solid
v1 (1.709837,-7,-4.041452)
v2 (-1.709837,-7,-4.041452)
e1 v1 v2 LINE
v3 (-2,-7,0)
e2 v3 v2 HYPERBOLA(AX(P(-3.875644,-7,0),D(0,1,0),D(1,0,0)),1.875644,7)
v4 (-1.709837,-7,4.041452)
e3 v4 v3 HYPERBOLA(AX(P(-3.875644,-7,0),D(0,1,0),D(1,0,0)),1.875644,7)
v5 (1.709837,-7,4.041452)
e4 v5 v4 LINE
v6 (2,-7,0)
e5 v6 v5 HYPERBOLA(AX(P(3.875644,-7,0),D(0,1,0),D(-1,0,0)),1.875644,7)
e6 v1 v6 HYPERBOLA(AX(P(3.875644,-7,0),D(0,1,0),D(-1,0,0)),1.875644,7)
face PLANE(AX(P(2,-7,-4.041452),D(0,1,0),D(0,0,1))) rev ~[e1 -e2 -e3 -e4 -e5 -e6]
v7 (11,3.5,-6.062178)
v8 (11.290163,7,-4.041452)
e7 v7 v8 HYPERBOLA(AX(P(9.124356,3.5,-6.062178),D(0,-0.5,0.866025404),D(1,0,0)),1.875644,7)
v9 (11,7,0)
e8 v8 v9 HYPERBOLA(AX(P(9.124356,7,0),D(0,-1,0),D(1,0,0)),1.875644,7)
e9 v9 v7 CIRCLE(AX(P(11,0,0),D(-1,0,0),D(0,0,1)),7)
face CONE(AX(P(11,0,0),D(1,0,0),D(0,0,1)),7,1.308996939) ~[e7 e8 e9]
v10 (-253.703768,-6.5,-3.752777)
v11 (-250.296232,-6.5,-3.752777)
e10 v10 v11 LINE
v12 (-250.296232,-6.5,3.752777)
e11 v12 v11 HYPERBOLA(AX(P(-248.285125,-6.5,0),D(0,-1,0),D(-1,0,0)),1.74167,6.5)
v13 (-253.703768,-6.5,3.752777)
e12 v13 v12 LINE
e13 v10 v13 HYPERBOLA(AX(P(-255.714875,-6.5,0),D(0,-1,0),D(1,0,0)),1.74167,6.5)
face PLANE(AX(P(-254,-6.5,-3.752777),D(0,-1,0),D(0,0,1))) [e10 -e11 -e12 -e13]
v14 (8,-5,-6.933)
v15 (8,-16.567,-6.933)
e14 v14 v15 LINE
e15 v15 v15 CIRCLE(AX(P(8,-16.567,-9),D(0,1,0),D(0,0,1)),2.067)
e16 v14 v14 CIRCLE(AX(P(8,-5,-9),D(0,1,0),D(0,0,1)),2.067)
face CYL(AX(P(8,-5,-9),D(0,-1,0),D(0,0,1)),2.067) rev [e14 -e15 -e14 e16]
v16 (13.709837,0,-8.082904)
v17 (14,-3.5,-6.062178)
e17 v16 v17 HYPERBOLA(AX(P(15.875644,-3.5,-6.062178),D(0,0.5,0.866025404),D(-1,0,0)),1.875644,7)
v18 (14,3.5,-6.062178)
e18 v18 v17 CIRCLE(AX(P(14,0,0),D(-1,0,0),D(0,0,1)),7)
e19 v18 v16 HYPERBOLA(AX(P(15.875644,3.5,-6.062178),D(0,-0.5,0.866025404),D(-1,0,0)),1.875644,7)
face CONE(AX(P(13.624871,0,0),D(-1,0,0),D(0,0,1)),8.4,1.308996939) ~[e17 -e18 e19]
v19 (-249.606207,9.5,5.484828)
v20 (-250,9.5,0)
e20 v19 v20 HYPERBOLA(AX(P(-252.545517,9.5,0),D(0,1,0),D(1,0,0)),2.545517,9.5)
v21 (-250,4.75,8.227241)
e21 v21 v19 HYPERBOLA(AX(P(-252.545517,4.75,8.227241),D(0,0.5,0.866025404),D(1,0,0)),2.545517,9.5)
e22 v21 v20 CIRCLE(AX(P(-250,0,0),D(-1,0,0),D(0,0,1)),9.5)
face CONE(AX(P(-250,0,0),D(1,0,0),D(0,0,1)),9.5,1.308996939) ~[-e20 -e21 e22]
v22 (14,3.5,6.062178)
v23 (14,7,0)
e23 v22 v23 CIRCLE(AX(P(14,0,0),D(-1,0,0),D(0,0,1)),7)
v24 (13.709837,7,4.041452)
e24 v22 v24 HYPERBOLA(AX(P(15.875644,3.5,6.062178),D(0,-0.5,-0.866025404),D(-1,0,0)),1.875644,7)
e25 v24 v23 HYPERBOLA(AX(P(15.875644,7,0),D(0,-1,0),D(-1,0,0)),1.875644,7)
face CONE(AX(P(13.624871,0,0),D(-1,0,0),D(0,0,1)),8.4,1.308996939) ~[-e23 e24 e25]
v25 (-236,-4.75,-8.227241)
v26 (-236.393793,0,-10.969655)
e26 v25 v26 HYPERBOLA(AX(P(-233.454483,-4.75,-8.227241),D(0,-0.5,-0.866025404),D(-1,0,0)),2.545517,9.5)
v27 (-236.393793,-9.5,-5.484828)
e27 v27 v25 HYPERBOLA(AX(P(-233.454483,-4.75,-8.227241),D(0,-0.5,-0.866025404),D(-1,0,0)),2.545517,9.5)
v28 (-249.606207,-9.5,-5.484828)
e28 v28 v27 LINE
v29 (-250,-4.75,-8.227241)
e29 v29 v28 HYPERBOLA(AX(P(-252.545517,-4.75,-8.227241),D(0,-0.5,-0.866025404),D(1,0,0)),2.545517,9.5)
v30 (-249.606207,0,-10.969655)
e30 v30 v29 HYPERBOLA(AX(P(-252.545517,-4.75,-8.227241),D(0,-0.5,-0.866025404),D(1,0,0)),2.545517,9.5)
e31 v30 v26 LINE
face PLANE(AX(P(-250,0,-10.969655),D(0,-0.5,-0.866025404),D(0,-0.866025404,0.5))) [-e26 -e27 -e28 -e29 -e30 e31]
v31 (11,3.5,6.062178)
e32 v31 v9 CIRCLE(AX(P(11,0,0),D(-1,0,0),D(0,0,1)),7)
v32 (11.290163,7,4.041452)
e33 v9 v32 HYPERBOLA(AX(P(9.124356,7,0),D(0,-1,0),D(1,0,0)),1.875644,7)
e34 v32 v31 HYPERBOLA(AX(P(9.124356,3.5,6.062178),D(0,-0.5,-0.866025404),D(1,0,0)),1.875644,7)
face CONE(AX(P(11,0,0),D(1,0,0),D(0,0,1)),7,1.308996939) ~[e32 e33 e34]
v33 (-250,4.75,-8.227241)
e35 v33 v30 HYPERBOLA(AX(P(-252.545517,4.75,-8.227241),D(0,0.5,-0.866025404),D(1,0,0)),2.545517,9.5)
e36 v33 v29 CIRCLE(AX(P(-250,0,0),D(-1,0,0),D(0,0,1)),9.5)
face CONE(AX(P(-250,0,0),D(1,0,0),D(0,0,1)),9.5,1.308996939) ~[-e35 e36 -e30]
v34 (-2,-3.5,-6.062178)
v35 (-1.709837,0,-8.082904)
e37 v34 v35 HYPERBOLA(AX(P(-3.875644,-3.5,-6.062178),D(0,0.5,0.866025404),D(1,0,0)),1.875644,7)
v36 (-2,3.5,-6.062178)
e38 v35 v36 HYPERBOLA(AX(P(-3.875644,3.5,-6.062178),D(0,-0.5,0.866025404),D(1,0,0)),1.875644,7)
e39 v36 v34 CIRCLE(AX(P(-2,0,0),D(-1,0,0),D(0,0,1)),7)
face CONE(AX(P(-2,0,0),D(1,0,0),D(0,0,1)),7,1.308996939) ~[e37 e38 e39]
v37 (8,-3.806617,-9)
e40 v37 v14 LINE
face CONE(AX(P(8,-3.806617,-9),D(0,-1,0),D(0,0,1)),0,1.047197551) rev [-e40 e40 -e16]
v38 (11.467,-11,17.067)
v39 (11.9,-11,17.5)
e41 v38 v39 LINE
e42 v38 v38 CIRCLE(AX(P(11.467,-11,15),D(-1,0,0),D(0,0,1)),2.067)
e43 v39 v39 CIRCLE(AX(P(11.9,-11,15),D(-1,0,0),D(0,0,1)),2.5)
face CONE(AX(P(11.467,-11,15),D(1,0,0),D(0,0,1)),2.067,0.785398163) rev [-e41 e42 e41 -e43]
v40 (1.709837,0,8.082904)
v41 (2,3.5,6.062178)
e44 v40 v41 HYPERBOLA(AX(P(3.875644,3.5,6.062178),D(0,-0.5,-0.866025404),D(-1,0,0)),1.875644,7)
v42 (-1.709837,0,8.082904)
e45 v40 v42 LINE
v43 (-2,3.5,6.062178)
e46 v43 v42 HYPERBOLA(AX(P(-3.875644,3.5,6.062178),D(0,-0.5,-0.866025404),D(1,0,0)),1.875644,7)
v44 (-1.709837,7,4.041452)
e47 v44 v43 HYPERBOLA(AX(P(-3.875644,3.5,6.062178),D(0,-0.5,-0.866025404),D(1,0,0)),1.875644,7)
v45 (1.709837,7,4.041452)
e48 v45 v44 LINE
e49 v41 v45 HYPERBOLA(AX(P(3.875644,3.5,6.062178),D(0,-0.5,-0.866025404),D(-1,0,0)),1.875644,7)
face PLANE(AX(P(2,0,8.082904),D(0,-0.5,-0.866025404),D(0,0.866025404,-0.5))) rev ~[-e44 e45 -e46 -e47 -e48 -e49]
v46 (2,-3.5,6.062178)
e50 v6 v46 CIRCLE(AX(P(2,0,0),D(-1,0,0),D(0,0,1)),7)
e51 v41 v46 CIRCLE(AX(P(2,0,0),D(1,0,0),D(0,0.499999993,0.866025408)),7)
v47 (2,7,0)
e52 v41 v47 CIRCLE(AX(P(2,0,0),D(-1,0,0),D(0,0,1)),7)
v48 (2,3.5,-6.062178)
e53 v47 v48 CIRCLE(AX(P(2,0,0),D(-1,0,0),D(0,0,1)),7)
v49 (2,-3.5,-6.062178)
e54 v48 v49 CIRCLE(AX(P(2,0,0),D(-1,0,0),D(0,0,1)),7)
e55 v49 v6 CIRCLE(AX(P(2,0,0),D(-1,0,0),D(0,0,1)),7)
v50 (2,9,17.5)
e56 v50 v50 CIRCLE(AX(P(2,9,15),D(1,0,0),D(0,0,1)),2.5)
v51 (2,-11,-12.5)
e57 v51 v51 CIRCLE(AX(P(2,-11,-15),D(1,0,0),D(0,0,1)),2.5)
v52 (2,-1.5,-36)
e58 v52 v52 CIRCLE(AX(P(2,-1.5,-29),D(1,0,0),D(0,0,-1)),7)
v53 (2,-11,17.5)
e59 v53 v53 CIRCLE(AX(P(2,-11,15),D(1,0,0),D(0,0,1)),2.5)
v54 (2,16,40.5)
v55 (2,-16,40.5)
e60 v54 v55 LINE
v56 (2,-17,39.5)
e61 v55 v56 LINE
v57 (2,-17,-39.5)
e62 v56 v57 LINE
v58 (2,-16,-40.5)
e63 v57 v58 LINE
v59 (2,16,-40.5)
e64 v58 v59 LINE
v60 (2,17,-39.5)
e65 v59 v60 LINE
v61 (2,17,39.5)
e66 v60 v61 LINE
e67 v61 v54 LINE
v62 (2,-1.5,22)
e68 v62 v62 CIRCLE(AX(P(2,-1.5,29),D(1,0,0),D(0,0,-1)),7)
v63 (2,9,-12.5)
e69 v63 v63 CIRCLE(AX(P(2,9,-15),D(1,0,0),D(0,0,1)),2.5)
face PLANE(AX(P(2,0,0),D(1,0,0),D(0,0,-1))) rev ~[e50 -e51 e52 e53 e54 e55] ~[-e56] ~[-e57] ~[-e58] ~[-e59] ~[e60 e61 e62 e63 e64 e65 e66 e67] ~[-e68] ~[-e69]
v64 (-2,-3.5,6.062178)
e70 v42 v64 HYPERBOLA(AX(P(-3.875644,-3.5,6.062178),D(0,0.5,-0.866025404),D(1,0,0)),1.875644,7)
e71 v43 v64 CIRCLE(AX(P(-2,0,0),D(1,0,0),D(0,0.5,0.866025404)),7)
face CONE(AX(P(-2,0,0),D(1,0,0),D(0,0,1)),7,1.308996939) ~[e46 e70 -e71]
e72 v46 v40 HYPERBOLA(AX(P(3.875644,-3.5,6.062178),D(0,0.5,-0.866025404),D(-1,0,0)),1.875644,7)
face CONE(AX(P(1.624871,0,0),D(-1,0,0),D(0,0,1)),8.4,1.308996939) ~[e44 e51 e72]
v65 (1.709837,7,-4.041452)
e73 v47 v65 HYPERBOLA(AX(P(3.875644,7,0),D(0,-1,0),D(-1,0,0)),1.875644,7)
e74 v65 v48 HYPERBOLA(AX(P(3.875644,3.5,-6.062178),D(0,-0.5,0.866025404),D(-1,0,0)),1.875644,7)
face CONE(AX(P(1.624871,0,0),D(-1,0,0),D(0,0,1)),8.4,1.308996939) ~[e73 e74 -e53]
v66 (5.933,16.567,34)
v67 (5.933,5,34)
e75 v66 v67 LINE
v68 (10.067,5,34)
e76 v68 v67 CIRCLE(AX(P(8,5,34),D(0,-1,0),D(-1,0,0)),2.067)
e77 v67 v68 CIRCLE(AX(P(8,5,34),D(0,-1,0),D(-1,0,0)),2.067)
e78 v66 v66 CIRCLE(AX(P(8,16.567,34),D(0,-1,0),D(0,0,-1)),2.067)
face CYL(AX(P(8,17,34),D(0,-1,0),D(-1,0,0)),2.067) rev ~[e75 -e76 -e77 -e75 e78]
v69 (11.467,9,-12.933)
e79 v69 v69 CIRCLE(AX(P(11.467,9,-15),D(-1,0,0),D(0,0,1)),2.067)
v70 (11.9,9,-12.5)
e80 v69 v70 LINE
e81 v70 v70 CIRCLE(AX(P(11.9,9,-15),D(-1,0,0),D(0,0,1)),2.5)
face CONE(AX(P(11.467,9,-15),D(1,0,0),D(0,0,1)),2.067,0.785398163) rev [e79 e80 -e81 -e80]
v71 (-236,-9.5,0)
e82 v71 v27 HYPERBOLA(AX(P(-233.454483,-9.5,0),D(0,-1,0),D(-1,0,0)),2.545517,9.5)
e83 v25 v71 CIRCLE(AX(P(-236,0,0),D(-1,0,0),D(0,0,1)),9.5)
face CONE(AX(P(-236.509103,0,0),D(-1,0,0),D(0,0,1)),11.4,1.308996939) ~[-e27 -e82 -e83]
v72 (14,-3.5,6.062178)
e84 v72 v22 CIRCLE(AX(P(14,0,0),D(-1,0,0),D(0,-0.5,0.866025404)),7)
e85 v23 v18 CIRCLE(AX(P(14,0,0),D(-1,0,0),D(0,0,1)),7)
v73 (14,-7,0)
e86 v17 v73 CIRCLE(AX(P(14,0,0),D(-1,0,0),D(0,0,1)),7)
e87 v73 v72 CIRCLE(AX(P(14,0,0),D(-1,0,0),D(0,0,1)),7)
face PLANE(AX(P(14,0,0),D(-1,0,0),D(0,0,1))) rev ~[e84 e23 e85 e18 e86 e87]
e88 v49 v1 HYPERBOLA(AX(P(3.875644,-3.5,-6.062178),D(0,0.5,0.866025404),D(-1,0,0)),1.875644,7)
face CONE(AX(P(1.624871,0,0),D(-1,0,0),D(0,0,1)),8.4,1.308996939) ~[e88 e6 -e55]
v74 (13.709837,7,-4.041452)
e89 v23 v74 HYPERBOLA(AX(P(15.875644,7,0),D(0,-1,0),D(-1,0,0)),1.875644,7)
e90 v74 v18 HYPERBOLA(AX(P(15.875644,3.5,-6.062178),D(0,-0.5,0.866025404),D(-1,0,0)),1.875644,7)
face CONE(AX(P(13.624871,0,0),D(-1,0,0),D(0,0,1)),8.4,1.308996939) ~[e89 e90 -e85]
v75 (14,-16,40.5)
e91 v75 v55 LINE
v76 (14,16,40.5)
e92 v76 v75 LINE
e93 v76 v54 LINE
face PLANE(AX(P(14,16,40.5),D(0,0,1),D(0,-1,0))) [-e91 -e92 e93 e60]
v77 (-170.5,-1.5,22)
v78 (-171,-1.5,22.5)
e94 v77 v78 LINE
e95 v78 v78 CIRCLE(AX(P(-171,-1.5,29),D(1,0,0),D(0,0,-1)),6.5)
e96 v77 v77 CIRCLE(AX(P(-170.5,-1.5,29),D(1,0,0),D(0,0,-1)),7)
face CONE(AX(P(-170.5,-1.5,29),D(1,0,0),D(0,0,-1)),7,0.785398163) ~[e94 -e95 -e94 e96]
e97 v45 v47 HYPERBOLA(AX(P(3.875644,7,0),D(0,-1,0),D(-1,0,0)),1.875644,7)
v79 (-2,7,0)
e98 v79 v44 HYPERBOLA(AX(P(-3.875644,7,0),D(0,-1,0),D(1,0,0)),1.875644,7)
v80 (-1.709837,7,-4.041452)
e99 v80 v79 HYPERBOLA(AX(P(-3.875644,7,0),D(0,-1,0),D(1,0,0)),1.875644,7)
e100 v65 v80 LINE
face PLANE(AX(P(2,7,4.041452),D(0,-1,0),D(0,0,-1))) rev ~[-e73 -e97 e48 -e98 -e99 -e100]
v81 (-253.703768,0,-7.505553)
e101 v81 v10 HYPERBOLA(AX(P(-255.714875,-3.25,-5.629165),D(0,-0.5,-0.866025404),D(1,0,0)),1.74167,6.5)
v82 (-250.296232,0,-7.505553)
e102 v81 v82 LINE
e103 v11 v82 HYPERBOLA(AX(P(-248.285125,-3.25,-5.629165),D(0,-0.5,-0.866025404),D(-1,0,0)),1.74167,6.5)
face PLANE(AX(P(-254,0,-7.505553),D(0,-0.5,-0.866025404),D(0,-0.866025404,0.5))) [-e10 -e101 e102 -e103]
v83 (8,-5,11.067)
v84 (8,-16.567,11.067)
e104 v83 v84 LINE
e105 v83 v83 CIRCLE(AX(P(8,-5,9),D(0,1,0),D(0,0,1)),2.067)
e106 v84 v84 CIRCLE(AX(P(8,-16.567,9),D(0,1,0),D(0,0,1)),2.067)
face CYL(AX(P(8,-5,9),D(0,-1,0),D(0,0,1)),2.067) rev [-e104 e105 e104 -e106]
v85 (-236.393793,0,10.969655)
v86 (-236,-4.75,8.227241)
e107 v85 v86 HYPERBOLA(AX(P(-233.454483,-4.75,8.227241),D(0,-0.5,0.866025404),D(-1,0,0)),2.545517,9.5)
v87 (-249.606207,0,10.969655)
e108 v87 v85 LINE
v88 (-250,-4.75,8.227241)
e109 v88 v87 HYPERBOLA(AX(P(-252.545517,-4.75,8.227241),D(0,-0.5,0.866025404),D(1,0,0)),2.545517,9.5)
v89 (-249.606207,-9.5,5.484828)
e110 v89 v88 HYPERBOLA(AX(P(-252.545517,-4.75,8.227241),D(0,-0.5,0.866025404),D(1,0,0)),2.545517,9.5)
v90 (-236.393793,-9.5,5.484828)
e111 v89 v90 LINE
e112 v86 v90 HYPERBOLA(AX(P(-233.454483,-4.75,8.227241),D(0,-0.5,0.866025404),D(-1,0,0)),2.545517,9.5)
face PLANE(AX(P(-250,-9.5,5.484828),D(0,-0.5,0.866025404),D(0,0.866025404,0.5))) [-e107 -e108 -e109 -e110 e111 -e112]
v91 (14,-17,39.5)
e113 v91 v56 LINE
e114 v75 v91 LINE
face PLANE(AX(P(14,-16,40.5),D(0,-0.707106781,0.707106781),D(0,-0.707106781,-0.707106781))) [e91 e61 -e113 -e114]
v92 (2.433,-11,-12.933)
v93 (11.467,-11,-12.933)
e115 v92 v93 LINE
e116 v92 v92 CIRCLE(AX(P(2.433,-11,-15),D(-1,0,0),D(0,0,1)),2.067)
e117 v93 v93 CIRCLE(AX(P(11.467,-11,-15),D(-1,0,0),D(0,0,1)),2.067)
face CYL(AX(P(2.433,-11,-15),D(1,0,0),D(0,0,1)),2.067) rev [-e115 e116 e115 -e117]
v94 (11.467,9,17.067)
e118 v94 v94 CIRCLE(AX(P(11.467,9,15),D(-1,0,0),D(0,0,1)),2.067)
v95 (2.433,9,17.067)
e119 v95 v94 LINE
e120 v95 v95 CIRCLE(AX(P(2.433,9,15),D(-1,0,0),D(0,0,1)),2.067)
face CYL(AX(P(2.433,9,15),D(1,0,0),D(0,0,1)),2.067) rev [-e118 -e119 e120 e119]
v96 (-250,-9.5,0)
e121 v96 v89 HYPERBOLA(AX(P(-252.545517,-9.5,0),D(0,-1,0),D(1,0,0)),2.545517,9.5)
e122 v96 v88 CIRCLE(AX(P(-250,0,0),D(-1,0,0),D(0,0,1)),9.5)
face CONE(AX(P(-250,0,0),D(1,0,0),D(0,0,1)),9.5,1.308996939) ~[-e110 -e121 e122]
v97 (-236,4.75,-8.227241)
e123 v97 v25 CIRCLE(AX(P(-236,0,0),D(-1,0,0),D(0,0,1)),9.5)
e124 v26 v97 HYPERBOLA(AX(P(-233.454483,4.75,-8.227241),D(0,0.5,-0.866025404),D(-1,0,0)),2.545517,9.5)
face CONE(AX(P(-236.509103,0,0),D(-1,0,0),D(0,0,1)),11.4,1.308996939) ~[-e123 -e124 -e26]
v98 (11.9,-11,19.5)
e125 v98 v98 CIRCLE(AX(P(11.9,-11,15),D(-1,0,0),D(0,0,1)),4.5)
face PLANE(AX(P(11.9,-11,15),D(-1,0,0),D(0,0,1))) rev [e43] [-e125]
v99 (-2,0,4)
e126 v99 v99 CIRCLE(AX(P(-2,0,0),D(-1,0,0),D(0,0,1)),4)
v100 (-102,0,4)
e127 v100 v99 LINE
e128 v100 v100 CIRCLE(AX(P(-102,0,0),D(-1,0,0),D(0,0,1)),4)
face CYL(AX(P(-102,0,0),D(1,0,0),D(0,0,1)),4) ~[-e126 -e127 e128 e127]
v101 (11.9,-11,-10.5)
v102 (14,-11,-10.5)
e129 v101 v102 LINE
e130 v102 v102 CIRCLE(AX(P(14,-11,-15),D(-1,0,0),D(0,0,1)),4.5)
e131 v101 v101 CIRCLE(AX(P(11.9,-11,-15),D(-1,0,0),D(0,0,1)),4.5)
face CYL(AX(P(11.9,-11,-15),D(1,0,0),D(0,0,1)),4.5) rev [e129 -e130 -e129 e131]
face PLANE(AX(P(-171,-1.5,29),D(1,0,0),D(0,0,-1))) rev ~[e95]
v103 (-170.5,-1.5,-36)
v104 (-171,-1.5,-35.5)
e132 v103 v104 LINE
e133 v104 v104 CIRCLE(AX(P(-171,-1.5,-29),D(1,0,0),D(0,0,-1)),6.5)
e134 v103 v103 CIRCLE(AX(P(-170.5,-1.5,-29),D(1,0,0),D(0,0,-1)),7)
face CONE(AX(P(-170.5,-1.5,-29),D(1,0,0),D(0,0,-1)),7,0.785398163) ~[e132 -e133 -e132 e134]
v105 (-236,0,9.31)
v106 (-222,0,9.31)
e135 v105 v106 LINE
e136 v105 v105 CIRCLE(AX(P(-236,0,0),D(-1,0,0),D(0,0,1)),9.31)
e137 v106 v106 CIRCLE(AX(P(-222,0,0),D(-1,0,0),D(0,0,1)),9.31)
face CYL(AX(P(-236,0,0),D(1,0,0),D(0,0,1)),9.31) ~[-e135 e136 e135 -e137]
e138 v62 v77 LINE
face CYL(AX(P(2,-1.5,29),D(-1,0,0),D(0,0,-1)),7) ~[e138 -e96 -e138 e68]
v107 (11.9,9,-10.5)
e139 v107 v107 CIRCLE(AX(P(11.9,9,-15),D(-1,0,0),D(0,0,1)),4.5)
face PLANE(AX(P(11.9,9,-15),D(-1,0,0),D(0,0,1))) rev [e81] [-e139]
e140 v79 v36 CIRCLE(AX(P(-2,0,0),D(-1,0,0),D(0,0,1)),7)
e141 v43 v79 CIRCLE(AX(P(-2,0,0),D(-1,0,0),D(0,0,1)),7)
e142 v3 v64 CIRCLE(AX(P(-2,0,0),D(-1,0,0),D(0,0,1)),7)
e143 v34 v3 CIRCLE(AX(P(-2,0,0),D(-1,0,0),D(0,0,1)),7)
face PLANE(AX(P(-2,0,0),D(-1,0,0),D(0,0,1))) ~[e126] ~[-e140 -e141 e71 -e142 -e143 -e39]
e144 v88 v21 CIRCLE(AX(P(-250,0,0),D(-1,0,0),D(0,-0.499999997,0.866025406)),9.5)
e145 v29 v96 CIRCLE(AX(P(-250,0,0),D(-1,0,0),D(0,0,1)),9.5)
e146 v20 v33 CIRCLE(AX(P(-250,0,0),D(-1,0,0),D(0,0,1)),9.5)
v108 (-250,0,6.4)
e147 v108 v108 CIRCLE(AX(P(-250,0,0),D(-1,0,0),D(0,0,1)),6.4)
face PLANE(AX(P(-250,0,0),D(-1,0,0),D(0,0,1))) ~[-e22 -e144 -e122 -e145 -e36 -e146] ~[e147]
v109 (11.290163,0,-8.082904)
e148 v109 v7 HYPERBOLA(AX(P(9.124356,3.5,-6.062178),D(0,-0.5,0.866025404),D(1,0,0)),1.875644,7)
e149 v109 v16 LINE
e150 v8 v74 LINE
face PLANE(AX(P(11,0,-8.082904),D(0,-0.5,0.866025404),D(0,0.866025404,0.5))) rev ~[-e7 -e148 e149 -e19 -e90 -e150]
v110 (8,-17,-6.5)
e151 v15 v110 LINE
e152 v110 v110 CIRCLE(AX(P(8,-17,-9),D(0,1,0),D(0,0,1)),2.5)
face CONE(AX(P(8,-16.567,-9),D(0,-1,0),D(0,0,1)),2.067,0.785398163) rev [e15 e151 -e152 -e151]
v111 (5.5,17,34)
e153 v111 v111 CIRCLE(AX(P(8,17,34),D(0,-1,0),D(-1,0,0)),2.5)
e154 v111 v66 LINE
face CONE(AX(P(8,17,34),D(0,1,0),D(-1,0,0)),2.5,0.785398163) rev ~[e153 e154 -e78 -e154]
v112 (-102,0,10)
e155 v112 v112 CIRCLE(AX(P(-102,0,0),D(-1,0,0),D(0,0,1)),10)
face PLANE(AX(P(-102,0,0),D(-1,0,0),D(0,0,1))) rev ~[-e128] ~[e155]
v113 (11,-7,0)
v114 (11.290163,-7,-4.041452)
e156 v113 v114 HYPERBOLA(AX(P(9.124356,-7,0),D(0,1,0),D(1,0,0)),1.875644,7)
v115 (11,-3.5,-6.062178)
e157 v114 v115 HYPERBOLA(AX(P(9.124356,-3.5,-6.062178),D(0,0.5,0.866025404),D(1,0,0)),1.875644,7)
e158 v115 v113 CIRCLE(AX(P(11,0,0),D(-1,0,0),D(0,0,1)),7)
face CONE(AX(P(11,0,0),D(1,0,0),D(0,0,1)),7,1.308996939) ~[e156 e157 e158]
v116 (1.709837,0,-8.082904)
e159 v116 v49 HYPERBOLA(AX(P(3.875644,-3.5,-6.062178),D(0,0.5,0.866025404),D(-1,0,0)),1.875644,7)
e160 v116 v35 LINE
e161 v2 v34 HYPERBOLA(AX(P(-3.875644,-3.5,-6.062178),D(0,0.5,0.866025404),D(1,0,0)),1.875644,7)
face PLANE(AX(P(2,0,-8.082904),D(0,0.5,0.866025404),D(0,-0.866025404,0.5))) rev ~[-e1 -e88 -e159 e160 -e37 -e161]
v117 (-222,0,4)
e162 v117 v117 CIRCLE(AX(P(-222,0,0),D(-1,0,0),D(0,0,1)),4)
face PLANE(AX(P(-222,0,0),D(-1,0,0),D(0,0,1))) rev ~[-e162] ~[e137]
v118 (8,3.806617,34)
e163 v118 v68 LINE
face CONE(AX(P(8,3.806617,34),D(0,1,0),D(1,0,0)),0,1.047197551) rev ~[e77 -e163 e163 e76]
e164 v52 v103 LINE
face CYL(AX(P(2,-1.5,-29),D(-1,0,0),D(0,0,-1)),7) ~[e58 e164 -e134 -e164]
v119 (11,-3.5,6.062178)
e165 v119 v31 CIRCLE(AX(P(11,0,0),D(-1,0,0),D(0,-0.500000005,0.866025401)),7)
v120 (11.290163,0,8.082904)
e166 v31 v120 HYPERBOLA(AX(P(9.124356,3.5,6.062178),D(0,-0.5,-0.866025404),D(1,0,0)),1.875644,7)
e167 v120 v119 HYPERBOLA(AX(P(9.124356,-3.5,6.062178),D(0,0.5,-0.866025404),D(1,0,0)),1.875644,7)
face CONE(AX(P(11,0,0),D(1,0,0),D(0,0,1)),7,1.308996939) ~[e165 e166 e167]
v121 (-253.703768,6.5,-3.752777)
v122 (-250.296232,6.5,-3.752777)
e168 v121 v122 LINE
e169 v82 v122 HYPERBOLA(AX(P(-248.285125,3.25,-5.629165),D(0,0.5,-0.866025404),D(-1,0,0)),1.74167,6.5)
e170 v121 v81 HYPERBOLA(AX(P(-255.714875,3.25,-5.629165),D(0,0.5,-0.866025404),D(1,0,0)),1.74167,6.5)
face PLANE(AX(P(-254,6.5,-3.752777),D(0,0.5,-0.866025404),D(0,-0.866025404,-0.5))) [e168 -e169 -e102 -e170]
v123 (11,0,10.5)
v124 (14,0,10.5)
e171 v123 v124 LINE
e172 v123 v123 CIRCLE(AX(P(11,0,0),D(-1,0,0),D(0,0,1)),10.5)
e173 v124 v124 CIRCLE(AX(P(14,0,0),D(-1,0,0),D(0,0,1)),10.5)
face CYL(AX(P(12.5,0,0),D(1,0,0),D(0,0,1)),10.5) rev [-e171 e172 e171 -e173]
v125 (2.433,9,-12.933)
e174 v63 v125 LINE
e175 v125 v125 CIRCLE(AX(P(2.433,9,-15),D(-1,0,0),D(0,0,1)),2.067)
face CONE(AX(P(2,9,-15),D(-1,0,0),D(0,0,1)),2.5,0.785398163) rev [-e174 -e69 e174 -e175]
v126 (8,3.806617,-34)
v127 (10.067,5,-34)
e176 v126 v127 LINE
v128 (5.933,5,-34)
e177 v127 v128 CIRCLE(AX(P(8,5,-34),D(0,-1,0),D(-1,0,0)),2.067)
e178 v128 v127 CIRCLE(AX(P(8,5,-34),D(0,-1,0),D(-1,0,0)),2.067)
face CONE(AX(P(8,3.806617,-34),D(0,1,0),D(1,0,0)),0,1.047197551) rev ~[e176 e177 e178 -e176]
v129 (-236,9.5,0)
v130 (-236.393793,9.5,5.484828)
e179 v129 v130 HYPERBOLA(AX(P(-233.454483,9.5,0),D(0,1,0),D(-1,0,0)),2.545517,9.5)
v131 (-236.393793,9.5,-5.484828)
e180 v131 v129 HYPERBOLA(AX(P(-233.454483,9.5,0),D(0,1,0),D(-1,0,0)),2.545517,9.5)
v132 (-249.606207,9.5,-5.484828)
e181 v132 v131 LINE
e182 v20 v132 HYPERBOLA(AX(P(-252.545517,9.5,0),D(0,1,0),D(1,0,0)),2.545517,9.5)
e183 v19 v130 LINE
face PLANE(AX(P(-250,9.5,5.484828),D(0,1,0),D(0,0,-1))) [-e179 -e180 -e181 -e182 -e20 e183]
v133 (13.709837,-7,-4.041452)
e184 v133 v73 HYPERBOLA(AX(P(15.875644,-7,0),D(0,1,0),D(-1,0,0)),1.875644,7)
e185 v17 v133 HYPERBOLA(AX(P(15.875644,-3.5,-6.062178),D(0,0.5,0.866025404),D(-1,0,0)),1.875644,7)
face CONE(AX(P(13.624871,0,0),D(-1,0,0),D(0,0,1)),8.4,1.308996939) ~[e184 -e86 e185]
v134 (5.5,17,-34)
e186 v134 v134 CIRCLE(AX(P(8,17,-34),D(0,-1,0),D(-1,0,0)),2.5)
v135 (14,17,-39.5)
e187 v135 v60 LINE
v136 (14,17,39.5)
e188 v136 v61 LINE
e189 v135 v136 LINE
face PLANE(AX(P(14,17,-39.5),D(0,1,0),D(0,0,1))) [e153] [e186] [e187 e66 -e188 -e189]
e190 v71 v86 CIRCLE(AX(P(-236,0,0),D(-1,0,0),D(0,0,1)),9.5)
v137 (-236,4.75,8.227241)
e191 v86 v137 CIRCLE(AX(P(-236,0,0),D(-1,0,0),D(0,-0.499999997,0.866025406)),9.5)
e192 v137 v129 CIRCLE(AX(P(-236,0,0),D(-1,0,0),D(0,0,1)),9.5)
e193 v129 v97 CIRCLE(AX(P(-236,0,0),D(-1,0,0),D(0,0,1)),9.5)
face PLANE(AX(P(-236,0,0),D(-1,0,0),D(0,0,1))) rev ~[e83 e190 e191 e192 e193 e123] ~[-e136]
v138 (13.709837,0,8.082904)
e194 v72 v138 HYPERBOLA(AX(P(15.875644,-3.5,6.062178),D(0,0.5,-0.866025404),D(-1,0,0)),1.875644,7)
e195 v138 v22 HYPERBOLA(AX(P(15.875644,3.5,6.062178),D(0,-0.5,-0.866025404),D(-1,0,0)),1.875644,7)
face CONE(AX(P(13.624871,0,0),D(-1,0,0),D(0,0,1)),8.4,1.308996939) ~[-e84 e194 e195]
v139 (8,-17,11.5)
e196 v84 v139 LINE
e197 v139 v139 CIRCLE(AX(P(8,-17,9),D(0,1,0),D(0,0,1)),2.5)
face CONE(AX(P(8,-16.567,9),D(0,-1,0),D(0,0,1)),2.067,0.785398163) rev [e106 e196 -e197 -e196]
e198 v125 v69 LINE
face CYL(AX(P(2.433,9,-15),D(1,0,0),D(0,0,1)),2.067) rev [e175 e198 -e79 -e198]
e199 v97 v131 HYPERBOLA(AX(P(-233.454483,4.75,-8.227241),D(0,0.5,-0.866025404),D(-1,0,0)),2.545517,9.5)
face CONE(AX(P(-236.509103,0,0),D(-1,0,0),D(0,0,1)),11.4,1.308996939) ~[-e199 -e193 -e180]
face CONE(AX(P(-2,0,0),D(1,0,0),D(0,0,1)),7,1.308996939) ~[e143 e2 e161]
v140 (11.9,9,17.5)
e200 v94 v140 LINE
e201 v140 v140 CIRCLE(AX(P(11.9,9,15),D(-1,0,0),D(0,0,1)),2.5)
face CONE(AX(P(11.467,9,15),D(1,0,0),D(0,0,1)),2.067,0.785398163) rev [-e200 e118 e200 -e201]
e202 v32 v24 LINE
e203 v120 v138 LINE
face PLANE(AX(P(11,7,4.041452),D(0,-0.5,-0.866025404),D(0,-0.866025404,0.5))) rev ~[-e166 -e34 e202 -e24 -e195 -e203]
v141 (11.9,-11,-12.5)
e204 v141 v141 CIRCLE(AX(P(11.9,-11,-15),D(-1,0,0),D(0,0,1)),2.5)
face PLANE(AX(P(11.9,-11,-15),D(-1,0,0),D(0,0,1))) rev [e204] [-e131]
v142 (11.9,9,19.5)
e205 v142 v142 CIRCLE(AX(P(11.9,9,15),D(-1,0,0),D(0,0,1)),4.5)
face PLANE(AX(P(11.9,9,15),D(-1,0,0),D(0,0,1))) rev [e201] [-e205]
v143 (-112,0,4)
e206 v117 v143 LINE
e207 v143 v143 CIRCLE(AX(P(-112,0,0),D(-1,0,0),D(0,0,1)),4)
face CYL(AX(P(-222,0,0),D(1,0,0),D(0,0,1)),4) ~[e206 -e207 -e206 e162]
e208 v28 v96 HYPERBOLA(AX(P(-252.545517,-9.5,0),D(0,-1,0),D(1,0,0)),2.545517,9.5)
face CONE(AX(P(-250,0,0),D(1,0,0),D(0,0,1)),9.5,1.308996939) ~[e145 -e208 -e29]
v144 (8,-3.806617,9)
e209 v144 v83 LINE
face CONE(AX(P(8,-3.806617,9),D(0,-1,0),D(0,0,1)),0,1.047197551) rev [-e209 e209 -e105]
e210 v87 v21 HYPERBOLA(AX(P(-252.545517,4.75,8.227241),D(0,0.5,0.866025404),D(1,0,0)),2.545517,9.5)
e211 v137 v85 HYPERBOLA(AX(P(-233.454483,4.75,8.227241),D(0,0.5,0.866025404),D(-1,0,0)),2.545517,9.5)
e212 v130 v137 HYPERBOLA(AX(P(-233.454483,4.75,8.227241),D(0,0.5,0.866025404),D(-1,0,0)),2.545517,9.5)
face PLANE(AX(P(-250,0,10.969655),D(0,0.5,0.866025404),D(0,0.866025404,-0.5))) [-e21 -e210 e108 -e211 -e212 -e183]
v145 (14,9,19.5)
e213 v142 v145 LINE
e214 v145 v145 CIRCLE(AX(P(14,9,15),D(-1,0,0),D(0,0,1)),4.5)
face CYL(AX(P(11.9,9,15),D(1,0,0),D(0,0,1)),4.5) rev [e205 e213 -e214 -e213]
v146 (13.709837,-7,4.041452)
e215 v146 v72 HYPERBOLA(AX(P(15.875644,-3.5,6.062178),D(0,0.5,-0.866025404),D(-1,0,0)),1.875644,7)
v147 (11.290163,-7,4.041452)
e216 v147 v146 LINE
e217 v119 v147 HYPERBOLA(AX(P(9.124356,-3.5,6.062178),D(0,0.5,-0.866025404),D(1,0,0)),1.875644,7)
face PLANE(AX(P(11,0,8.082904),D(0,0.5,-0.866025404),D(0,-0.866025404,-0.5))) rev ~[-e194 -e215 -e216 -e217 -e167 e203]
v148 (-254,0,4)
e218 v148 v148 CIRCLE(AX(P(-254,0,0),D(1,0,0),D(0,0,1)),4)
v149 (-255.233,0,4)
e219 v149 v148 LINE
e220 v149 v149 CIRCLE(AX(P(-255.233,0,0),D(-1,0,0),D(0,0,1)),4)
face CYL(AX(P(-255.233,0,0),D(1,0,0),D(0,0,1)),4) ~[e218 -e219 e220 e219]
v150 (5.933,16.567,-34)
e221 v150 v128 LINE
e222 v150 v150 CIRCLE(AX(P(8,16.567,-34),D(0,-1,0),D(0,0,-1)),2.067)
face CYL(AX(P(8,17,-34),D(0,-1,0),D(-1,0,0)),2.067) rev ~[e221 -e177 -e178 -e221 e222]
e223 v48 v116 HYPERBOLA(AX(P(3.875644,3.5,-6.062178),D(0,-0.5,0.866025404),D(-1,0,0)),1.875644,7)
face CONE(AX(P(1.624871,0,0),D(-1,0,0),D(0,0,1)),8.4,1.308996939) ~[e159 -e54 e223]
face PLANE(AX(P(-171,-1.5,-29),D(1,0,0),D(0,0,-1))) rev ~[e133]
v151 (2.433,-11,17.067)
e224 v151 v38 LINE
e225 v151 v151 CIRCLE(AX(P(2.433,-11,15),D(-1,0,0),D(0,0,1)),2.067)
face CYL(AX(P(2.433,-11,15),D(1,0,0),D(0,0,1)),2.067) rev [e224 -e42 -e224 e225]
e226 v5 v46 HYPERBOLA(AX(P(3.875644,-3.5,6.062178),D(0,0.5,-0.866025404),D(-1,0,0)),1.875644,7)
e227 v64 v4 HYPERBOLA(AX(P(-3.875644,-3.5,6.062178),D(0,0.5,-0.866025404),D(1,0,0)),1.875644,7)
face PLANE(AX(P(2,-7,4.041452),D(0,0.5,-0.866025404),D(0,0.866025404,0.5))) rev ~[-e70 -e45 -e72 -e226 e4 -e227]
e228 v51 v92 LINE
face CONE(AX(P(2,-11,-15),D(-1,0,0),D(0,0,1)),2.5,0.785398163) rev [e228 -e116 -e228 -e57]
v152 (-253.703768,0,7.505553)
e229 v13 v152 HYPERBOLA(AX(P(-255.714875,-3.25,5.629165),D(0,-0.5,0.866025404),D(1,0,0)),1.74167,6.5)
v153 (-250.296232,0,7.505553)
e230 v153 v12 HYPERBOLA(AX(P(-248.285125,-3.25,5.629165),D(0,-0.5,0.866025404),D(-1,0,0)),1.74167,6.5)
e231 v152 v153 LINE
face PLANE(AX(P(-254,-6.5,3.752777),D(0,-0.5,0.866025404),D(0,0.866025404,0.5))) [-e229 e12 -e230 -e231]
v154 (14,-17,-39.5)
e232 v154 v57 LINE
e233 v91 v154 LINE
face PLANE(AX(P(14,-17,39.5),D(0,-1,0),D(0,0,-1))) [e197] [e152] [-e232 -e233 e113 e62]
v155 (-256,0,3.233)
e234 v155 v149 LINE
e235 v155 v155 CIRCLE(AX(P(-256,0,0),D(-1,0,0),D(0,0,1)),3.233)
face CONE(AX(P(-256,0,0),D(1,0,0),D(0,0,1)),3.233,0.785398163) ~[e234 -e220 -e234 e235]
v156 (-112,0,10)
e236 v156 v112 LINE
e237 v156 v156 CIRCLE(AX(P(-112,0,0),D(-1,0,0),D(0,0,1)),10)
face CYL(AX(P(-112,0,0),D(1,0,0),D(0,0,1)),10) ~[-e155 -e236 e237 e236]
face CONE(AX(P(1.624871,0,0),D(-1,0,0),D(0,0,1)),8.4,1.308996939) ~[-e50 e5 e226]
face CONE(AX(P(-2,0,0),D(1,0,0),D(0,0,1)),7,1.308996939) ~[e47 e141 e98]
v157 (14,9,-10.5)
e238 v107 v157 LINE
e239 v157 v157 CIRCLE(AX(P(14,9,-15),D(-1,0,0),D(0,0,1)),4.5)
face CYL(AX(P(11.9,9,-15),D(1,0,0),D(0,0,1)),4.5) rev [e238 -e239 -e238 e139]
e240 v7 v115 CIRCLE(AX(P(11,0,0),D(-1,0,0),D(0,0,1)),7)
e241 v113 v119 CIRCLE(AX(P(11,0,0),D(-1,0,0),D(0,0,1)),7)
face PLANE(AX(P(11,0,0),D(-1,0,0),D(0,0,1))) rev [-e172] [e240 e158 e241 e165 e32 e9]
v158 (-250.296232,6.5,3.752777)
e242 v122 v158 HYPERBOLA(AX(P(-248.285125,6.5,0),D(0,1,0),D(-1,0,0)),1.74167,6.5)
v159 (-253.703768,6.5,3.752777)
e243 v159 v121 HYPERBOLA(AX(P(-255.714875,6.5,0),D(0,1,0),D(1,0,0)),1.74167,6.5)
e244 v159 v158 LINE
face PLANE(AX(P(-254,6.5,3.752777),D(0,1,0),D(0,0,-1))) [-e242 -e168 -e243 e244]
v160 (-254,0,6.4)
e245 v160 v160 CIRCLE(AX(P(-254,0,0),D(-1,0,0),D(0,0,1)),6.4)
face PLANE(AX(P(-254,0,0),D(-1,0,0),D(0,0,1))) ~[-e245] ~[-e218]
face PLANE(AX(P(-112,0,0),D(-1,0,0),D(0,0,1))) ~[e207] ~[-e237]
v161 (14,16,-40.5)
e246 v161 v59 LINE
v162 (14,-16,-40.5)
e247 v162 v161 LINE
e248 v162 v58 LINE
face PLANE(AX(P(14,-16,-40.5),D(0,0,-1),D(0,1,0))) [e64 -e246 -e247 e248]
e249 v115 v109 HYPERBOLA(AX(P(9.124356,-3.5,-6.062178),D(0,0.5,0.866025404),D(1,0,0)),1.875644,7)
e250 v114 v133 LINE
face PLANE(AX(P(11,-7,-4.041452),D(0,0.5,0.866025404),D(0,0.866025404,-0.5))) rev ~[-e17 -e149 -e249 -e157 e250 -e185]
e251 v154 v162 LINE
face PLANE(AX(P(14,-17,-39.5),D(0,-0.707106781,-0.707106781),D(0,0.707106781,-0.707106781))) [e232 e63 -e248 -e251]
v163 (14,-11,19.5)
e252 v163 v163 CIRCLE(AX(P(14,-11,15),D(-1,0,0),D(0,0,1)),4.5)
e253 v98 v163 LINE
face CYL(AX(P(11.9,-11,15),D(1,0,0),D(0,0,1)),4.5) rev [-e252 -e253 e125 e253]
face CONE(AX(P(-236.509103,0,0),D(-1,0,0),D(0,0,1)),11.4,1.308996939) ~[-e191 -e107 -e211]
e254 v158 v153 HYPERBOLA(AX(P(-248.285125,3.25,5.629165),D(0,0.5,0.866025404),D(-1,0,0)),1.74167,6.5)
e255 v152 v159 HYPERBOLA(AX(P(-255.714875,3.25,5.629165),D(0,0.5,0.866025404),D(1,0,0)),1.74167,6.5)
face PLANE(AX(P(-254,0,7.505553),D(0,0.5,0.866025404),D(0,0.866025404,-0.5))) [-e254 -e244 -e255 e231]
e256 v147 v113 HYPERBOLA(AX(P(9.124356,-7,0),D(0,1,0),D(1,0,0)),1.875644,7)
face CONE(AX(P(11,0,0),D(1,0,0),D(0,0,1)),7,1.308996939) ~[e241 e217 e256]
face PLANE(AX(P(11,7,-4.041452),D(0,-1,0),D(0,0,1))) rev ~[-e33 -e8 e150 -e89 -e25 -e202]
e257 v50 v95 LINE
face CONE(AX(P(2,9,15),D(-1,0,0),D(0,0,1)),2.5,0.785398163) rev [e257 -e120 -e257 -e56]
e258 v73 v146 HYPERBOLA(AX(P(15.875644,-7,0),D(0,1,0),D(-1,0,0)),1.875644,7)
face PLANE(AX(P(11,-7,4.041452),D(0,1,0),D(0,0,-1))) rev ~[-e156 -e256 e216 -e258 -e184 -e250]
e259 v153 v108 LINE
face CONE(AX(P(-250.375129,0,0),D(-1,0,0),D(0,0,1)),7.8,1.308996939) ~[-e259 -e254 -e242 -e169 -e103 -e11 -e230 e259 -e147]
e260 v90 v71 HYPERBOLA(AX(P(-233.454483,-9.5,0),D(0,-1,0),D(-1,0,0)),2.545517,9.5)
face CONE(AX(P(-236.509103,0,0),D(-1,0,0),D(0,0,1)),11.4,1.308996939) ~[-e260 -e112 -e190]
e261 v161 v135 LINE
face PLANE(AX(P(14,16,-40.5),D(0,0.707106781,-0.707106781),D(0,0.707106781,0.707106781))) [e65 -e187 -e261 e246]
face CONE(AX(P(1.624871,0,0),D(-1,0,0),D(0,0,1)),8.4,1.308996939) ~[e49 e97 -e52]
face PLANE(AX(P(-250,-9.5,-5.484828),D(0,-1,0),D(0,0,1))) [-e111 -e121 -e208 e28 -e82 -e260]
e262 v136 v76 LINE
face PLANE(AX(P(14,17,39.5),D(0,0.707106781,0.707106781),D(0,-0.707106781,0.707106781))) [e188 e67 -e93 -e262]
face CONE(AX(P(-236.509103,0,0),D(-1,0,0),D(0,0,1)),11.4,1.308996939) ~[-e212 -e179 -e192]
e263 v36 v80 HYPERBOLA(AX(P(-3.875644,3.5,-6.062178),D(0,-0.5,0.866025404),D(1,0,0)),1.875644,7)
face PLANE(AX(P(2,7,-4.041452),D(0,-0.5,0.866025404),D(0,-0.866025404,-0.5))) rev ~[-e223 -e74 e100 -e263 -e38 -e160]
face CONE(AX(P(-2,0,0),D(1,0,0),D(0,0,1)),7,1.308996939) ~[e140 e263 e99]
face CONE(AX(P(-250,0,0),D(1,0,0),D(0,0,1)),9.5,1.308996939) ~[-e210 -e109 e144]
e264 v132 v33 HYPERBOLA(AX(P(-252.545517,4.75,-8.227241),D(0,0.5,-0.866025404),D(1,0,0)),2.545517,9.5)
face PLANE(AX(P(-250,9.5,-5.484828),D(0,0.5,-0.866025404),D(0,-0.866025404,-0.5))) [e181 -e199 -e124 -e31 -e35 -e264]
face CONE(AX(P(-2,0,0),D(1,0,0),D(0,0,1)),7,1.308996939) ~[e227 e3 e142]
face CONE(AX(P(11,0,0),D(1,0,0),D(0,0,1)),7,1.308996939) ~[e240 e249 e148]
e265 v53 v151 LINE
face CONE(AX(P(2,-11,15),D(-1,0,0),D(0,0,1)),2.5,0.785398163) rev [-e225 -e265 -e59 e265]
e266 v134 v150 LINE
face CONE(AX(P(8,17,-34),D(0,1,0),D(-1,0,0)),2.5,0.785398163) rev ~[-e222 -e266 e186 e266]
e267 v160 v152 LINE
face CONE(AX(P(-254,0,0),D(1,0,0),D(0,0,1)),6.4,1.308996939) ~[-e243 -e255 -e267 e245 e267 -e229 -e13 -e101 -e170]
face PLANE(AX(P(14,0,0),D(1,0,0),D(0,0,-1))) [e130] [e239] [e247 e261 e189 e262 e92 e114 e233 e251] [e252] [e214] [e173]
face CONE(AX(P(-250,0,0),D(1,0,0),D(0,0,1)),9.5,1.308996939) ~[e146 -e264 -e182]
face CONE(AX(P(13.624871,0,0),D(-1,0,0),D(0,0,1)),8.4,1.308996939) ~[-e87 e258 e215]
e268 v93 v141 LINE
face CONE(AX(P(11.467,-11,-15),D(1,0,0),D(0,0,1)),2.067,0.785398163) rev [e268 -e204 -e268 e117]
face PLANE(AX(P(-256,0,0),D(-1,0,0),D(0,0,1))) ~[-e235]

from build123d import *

# Parameters (mm, degrees)
BOSS_EXTRUDE1_DEPTH     = 12
CUT_EXTRUDE1_DEPTH      = 4
CUT_EXTRUDE1_DEPTH_BACK = 4
SKETCH9_W               = 28
SKETCH9_H               = 28
SKETCH10_W              = 3
SKETCH10_H              = 10.5
HOLE1_D                 = 4.134
HOLE1_DEPTH             = 12
HOLE1_CSINK_D           = 5
HOLE1_CSINK_ANGLE       = 90
HOLE1_TIP               = 1.193383006
HOLE2_D                 = 4.134
HOLE2_DEPTH             = 12
HOLE2_CSINK_D           = 5
HOLE2_CSINK_ANGLE       = 90
HOLE2_TIP               = 1.193383006
CUT_EXTRUDE2_DEPTH      = 3
CUT_EXTRUDE2_DEPTH_BACK = 3
SKETCH18_R              = 9.8
SKETCH21_W              = 38
SKETCH21_H              = 38
CUT_EXTRUDE3_DEPTH      = 14
SKETCH22_R              = 13
CUT_EXTRUDE4_DEPTH      = 4


with BuildPart() as part:
    # Sketch1 → Boss-Extrude1 (new body)
    with BuildSketch(Plane(origin=(14, 0, 0), x_dir=(0, 0, -1), z_dir=(1, 0, 0))):
        Polygon((-40.5, -16), (-39.5, -17), (39.5, -17), (40.5, -16), (40.5, 16), (39.5, 17), (-39.5, 17), (-40.5, 16), align=None)
    extrude(amount=-BOSS_EXTRUDE1_DEPTH)

    # Sketch2 → Revolve1 (revolve)
    with BuildSketch(Plane(origin=(0, -1.5, 0), x_dir=(1, 0, 0), z_dir=(0, 1, 0)), mode=Mode.PRIVATE) as revolve1_sk:
        Polygon((2, -29), (2, -36), (-170.5, -36), (-171, -35.5), (-171, -29), align=None)
    revolve(revolve1_sk.sketch.rotate(Axis((-171, -1.5, 29), (1, 0, 0)), 180), axis=Axis((-171, -1.5, 29), (1, 0, 0)))

    # Sketch3 → Revolve2 (revolve)
    with BuildSketch(Plane(origin=(0, -1.5, 0), x_dir=(1, 0, 0), z_dir=(0, 1, 0)), mode=Mode.PRIVATE) as revolve2_sk:
        Polygon((2, 29), (2, 22), (-170.5, 22), (-171, 22.5), (-171, 29), align=None)
    revolve(revolve2_sk.sketch.rotate(Axis((-171, -1.5, -29), (1, 0, 0)), 180), axis=Axis((-171, -1.5, -29), (1, 0, 0)))

    # Sketch4 → Cut-Revolve1 (revolve, cut)
    with BuildSketch(Plane(origin=(0, -11, 0), x_dir=(1, 0, 0), z_dir=(0, 1, 0)), mode=Mode.PRIVATE) as cut_revolve1_sk:
        Polygon((2, -15), (2, -12.5), (2.433, -12.933), (11.467, -12.933), (11.9, -12.5), (11.9, -10.5), (14, -10.5), (14, -15), align=None)
    revolve(cut_revolve1_sk.sketch.rotate(Axis((11.9, -11, 15), (-1, 0, 0)), 180), axis=Axis((11.9, -11, 15), (-1, 0, 0)), mode=Mode.SUBTRACT)

    # Sketch5 → Cut-Revolve2 (revolve, cut)
    with BuildSketch(Plane(origin=(0, -11, 0), x_dir=(1, 0, 0), z_dir=(0, 1, 0)), mode=Mode.PRIVATE) as cut_revolve2_sk:
        Polygon((2, 15), (2, 17.5), (2.433, 17.067), (11.467, 17.067), (11.9, 17.5), (11.9, 19.5), (14, 19.5), (14, 15), align=None)
    revolve(cut_revolve2_sk.sketch.rotate(Axis((11.9, -11, -15), (-1, 0, 0)), 180), axis=Axis((11.9, -11, -15), (-1, 0, 0)), mode=Mode.SUBTRACT)

    # Sketch6 → Cut-Revolve3 (revolve, cut)
    with BuildSketch(Plane(origin=(0, 9, 0), x_dir=(1, 0, 0), z_dir=(0, 1, 0)), mode=Mode.PRIVATE) as cut_revolve3_sk:
        Polygon((2, -15), (2, -12.5), (2.433, -12.933), (11.467, -12.933), (11.9, -12.5), (11.9, -10.5), (14, -10.5), (14, -15), align=None)
    revolve(cut_revolve3_sk.sketch.rotate(Axis((11.9, 9, 15), (-1, 0, 0)), 180), axis=Axis((11.9, 9, 15), (-1, 0, 0)), mode=Mode.SUBTRACT)

    # Sketch7 → Cut-Revolve4 (revolve, cut)
    with BuildSketch(Plane(origin=(0, 9, 0), x_dir=(1, 0, 0), z_dir=(0, 1, 0)), mode=Mode.PRIVATE) as cut_revolve4_sk:
        Polygon((2, 15), (2, 17.5), (2.433, 17.067), (11.467, 17.067), (11.9, 17.5), (11.9, 19.5), (14, 19.5), (14, 15), align=None)
    revolve(cut_revolve4_sk.sketch.rotate(Axis((11.9, 9, -15), (-1, 0, 0)), 180), axis=Axis((11.9, 9, -15), (-1, 0, 0)), mode=Mode.SUBTRACT)

    # Sketch8 → Revolve3 (revolve)
    with BuildSketch(Plane.XY, mode=Mode.PRIVATE) as revolve3_sk:
        Polygon((-112, 0), (-112, 10), (-102, 10), (-102, 4), (-2, 4), (-2, 7), (-1.624871131, 8.4), (1.624871131, 8.4), (2, 7), (2, 0), align=None)
    revolve(revolve3_sk.sketch.rotate(Axis((2, 0, 0), (-1, 0, 0)), 270), axis=Axis((2, 0, 0), (-1, 0, 0)))

    # Sketch9 → Cut-Extrude1 (cut, two sides: drawn at the far end of the back side and taken through both)
    with BuildSketch(Plane.ZY.offset(2).offset(-CUT_EXTRUDE1_DEPTH_BACK)):
        Rectangle(SKETCH9_W, SKETCH9_H)
        Polygon((4.041451884, -7), (8.082903769, 0), (4.041451884, 7), (-4.041451884, 7), (-8.082903769, 0), (-4.041451884, -7), align=None, mode=Mode.SUBTRACT)
    extrude(amount=CUT_EXTRUDE1_DEPTH + CUT_EXTRUDE1_DEPTH_BACK, mode=Mode.SUBTRACT)

    # Sketch10 → Cut-Revolve5 (revolve, cut)
    with BuildSketch(Plane.XY, mode=Mode.PRIVATE) as cut_revolve5_sk:
        with Locations((12.5, 5.25)):
            Rectangle(SKETCH10_W, SKETCH10_H)
    revolve(cut_revolve5_sk.sketch.rotate(Axis((14, 0, 0), (-1, 0, 0)), 270), axis=Axis((14, 0, 0), (-1, 0, 0)), mode=Mode.SUBTRACT)

    # Hole1
    with Locations(Plane(origin=(0, 17, 0), x_dir=(1, 0, 0), z_dir=(0, 1, 0))):
        with Locations((8, -34)):
            CounterSinkHole(HOLE1_D / 2, HOLE1_CSINK_D / 2, depth=HOLE1_DEPTH, counter_sink_angle=HOLE1_CSINK_ANGLE)
            with Locations((0, 0, -(HOLE1_DEPTH + HOLE1_TIP / 2))):  # 120° drill point
                Cone(0, HOLE1_D / 2, HOLE1_TIP, mode=Mode.SUBTRACT)

    # Hole2
    with Locations(Plane(origin=(0, 17, 0), x_dir=(1, 0, 0), z_dir=(0, 1, 0))):
        with Locations((8, 34)):
            CounterSinkHole(HOLE2_D / 2, HOLE2_CSINK_D / 2, depth=HOLE2_DEPTH, counter_sink_angle=HOLE2_CSINK_ANGLE)
            with Locations((0, 0, -(HOLE2_DEPTH + HOLE2_TIP / 2))):  # 120° drill point
                Cone(0, HOLE2_D / 2, HOLE2_TIP, mode=Mode.SUBTRACT)

    # Sketch16 → Cut-Revolve6 (revolve, cut)
    with BuildSketch(Plane(origin=(8, 0, 0), x_dir=(0, 0, -1), z_dir=(1, 0, 0)), mode=Mode.PRIVATE) as cut_revolve6_sk:
        Polygon((-9, -3.806616994), (-6.933, -5), (-6.933, -16.567), (-6.5, -17), (-9, -17), align=None)
    revolve(cut_revolve6_sk.sketch.rotate(Axis((8, -17, 9), (0, 1, 0)), 180), axis=Axis((8, -17, 9), (0, 1, 0)), mode=Mode.SUBTRACT)

    # Sketch17 → Cut-Revolve7 (revolve, cut)
    with BuildSketch(Plane(origin=(8, 0, 0), x_dir=(0, 0, -1), z_dir=(1, 0, 0)), mode=Mode.PRIVATE) as cut_revolve7_sk:
        Polygon((9, -3.806616994), (11.067, -5), (11.067, -16.567), (11.5, -17), (9, -17), align=None)
    revolve(cut_revolve7_sk.sketch.rotate(Axis((8, -17, -9), (0, 1, 0)), 180), axis=Axis((8, -17, -9), (0, 1, 0)), mode=Mode.SUBTRACT)

    # Sketch11 → Revolve4 (revolve)
    with BuildSketch(Plane.XY, mode=Mode.PRIVATE) as revolve4_sk:
        Polygon((11, 0), (11, 7), (11.375128869, 8.4), (13.624871131, 8.4), (14, 7), (14, 0), align=None)
    revolve(revolve4_sk.sketch.rotate(Axis((14, 0, 0), (-1, 0, 0)), 270), axis=Axis((14, 0, 0), (-1, 0, 0)))

    # Sketch18 → Cut-Extrude2 (cut, two sides: drawn at the far end of the back side and taken through both)
    with BuildSketch(Plane(origin=(14, 0, 0), x_dir=(0, 0, -1), z_dir=(1, 0, 0)).offset(-CUT_EXTRUDE2_DEPTH_BACK)):
        Circle(SKETCH18_R)
        Polygon((4.041451884, -7), (8.082903769, 0), (4.041451884, 7), (-4.041451884, 7), (-8.082903769, 0), (-4.041451884, -7), align=None, mode=Mode.SUBTRACT)
    extrude(amount=CUT_EXTRUDE2_DEPTH + CUT_EXTRUDE2_DEPTH_BACK, mode=Mode.SUBTRACT)

    # Sketch19 → Revolve5 (revolve)
    with BuildSketch(Plane.XY, mode=Mode.PRIVATE) as revolve5_sk:
        Polygon((-254, 0), (-254, 6.4), (-253.624871131, 7.8), (-250.375128869, 7.8), (-250, 6.4), (-250, 9.5), (-249.490896534, 11.4), (-236.509103466, 11.4), (-236, 9.5), (-236, 9.31), (-222, 9.31), (-222, 4), (-112, 4), (-112, 0), align=None)
    revolve(revolve5_sk.sketch.rotate(Axis((-112, 0, 0), (-1, 0, 0)), 270), axis=Axis((-112, 0, 0), (-1, 0, 0)))

    # Sketch20 → Revolve6 (revolve)
    with BuildSketch(Plane.XY, mode=Mode.PRIVATE) as revolve6_sk:
        Polygon((-256, 0), (-256, 3.233), (-255.233, 4), (-250, 4), (-250, 0), align=None)
    revolve(revolve6_sk.sketch.rotate(Axis((-250, 0, 0), (-1, 0, 0)), 270), axis=Axis((-250, 0, 0), (-1, 0, 0)))

    # Sketch21 → Cut-Extrude3 (cut)
    with BuildSketch(Plane.ZY.offset(250)):
        Rectangle(SKETCH21_W, SKETCH21_H)
        Polygon((5.484827557, -9.5), (10.969655115, 0), (5.484827557, 9.5), (-5.484827557, 9.5), (-10.969655115, 0), (-5.484827557, -9.5), align=None, mode=Mode.SUBTRACT)
    extrude(amount=-CUT_EXTRUDE3_DEPTH, mode=Mode.SUBTRACT)

    # Sketch22 → Cut-Extrude4 (cut)
    with BuildSketch(Plane.ZY.offset(254)):
        Circle(SKETCH22_R)
        Polygon((3.75277675, -6.5), (7.505553499, 0), (3.75277675, 6.5), (-3.75277675, 6.5), (-7.505553499, 0), (-3.75277675, -6.5), align=None, mode=Mode.SUBTRACT)
    extrude(amount=-CUT_EXTRUDE4_DEPTH, mode=Mode.SUBTRACT)


solid = part.part
